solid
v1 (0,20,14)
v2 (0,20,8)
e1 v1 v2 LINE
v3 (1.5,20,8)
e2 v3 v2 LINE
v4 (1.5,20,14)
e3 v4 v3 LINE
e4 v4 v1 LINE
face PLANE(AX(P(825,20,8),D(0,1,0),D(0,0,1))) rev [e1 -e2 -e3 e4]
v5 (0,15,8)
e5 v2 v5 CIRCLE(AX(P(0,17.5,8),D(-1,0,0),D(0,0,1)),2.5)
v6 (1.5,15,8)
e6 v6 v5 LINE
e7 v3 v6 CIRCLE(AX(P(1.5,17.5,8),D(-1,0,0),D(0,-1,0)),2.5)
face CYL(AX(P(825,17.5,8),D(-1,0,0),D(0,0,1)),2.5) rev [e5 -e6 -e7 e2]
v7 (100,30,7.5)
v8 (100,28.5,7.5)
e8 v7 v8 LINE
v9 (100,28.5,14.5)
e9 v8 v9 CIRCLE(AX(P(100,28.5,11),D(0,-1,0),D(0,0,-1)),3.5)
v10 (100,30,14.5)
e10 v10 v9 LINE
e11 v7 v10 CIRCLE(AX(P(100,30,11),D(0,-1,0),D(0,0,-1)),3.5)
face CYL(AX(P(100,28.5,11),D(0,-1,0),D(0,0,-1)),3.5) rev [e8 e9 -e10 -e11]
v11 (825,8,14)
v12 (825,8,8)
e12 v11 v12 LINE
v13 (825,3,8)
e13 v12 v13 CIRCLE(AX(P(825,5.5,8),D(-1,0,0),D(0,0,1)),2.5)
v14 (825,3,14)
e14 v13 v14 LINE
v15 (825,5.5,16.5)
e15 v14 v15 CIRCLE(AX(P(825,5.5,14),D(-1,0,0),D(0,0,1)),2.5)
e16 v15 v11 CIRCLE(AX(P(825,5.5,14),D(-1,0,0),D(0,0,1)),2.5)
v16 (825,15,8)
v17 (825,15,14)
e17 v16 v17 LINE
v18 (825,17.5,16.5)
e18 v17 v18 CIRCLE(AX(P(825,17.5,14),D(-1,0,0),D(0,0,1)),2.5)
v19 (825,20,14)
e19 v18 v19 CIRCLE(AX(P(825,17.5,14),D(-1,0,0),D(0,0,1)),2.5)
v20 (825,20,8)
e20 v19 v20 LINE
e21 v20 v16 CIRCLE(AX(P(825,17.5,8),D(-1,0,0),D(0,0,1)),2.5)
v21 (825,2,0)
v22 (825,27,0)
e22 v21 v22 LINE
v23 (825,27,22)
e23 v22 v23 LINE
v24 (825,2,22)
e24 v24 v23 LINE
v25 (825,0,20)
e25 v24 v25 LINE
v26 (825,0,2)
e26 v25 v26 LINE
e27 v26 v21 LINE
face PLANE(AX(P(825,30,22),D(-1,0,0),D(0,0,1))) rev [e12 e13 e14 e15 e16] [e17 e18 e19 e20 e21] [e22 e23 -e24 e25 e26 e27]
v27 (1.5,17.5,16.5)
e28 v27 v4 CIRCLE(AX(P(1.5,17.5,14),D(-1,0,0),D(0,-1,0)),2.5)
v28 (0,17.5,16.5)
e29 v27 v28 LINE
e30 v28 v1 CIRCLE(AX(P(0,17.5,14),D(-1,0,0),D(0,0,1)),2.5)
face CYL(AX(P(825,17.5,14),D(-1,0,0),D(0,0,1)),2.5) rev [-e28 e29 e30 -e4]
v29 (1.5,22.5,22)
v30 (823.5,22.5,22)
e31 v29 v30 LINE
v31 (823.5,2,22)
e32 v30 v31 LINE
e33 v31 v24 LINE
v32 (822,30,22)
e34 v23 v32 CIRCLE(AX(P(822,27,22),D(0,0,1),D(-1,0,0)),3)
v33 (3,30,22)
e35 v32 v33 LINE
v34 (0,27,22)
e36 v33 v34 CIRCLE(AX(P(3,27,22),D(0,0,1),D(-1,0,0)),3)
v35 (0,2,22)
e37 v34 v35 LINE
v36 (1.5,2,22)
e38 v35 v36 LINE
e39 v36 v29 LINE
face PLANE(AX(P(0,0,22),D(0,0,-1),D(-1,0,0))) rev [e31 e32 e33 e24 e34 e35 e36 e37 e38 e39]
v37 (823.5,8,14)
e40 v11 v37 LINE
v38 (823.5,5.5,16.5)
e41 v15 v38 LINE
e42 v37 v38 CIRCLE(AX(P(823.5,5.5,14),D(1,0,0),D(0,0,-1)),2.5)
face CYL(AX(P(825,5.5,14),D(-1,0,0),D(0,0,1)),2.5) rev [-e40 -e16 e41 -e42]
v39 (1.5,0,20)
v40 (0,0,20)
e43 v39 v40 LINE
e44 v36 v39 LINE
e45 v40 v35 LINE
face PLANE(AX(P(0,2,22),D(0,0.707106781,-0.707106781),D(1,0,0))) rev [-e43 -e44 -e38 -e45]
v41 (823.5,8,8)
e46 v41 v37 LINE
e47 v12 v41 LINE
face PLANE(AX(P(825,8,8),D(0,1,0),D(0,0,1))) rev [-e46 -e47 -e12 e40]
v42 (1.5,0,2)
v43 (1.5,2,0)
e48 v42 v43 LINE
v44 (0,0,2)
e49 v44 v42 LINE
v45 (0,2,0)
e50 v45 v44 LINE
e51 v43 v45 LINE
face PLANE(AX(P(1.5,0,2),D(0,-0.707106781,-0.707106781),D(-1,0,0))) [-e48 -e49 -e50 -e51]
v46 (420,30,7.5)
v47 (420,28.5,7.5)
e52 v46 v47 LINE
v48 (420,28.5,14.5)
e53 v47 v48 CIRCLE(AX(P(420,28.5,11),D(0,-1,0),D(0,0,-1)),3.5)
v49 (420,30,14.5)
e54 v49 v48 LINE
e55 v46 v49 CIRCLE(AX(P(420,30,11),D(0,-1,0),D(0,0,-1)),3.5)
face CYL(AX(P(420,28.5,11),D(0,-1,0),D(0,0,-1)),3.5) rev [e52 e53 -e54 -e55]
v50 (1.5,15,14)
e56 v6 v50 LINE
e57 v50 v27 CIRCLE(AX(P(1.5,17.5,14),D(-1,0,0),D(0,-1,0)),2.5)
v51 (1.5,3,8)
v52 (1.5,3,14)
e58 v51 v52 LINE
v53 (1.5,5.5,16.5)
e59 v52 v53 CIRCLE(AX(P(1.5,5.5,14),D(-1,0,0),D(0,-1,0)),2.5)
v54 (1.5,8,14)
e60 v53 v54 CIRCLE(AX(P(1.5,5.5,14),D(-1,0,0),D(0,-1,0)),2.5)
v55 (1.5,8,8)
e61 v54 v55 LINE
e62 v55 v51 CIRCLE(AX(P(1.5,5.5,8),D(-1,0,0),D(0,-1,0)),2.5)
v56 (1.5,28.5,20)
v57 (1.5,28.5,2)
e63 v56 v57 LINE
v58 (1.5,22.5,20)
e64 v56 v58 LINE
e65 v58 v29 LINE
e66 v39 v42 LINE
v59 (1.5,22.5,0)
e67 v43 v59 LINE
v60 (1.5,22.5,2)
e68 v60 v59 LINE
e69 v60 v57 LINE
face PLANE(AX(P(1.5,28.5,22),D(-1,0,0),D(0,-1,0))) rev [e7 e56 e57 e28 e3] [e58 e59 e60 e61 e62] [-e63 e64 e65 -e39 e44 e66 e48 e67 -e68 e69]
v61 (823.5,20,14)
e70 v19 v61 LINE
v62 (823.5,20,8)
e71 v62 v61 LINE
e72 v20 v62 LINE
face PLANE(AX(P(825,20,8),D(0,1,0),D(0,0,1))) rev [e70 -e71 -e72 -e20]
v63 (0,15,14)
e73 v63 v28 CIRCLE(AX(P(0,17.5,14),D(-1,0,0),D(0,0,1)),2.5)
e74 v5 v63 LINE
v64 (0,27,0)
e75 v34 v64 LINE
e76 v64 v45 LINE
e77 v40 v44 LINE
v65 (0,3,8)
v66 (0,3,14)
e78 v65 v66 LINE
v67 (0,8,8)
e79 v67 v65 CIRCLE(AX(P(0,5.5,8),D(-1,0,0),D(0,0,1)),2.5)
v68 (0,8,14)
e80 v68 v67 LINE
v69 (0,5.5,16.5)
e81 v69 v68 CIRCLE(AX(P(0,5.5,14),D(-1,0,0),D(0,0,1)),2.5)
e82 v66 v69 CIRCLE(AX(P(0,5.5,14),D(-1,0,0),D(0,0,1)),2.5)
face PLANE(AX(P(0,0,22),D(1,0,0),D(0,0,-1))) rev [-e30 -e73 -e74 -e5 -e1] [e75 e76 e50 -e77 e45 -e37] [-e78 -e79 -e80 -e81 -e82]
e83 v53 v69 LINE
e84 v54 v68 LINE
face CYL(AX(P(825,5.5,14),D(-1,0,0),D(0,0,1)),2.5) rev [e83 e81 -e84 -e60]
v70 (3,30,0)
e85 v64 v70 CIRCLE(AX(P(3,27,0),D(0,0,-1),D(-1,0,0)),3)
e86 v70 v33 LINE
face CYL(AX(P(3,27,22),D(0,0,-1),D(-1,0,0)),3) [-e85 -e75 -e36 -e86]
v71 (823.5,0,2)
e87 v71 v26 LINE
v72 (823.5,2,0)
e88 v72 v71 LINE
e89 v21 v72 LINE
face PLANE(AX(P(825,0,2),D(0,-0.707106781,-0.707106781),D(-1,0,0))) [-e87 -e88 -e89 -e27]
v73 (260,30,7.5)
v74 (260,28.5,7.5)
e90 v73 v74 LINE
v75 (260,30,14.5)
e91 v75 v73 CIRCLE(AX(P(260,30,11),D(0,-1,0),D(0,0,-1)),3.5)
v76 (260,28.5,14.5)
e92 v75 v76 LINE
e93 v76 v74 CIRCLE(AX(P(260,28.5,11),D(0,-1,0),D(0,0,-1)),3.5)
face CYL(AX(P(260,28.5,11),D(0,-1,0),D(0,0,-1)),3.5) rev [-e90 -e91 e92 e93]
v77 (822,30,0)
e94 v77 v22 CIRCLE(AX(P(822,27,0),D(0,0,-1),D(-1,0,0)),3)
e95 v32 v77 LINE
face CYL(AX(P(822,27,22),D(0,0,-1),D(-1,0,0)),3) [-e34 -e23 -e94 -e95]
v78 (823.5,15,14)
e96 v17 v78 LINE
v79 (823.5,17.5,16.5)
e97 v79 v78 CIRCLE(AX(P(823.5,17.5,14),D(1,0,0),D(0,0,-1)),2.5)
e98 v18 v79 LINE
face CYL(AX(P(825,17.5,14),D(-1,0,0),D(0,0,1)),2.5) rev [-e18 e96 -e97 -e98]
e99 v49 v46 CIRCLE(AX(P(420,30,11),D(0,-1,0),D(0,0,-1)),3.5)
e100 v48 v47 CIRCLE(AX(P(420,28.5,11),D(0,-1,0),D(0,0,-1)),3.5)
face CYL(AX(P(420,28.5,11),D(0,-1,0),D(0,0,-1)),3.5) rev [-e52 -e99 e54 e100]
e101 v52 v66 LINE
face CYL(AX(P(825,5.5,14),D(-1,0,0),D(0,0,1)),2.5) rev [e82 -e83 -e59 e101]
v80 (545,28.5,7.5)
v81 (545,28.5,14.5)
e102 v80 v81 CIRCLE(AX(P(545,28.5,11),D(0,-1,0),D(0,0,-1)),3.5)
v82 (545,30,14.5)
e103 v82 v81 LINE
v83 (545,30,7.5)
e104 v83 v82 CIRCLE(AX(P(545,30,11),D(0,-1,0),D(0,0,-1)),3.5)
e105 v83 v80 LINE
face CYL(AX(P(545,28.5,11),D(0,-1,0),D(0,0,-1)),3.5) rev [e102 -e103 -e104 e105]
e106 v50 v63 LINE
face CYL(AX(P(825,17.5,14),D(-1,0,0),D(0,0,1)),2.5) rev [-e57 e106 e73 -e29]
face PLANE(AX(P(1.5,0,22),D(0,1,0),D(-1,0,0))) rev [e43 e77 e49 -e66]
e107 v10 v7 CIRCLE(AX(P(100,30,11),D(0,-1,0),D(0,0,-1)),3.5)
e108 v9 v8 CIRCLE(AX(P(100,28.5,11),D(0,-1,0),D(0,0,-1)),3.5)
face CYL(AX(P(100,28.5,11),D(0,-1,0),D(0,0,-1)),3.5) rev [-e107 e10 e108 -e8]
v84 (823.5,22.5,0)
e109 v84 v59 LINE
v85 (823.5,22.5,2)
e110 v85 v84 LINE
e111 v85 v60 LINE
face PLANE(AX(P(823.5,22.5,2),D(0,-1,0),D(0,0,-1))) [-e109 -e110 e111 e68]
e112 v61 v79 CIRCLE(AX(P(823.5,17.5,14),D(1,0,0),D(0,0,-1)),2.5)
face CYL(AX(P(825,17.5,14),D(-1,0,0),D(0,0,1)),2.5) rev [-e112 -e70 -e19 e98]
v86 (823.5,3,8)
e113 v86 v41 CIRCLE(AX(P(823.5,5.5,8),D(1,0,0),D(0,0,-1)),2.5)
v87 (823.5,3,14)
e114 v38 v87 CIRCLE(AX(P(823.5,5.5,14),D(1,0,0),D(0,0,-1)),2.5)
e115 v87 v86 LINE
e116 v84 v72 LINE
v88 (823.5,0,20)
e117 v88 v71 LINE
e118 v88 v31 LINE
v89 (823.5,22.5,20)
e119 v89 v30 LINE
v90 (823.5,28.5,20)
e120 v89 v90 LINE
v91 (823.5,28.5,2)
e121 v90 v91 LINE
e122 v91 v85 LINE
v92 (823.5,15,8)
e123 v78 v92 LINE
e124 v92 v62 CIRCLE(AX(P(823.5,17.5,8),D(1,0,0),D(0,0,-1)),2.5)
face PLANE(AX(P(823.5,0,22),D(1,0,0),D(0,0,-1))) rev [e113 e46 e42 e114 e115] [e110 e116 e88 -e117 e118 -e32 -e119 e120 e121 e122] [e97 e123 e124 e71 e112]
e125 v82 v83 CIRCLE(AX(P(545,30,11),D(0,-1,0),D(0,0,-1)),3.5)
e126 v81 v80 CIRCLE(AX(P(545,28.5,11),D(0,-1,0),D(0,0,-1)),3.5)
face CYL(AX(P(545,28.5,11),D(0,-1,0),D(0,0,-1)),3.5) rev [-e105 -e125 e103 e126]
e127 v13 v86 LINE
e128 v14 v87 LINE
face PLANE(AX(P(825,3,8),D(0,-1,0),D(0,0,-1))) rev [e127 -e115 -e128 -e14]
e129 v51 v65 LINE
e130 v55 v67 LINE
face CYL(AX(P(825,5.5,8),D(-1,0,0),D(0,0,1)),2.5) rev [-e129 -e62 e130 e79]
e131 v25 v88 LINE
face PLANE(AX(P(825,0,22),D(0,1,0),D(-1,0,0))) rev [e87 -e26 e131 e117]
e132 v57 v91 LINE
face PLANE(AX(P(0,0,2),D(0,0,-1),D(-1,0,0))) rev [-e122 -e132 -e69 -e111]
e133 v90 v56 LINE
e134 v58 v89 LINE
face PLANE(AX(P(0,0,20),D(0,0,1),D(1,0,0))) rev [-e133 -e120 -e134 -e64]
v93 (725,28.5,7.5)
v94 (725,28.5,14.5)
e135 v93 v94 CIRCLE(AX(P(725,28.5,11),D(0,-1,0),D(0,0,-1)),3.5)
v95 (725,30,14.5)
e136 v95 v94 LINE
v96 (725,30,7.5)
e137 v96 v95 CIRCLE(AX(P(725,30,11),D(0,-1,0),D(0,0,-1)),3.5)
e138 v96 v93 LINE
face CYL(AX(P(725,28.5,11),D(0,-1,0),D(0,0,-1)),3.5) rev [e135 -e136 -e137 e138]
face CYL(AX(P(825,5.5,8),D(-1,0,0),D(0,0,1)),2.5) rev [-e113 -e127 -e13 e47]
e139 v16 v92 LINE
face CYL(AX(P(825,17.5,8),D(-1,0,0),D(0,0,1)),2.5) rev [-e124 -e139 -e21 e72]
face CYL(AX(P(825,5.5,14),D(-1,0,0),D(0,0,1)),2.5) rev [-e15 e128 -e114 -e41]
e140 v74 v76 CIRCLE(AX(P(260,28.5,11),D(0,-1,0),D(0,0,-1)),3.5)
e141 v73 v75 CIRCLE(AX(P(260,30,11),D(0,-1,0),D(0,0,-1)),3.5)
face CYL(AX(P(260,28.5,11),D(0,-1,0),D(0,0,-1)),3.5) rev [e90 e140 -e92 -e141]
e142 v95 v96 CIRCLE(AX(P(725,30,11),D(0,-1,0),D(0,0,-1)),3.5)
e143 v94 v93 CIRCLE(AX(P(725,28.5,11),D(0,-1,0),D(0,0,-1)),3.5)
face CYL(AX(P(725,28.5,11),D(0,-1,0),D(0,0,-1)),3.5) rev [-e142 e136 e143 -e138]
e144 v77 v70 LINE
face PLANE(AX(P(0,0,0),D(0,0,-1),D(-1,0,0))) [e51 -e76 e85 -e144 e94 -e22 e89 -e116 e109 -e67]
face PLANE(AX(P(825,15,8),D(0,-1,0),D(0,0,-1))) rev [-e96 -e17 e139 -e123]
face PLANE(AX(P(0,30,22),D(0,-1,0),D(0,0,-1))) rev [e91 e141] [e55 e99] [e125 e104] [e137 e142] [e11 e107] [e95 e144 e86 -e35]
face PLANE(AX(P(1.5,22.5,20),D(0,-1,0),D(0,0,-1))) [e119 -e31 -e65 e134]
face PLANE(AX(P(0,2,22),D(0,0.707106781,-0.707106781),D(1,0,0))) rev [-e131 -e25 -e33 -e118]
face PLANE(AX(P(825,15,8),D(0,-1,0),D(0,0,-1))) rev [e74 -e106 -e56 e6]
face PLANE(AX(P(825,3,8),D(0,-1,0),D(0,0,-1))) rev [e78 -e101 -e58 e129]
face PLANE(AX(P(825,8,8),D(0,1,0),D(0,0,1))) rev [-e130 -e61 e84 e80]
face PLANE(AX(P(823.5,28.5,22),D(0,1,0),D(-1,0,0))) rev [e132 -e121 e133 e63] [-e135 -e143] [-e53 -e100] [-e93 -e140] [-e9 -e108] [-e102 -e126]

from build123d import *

# Parameters (mm, degrees)
EXTRUDE_1_DEPTH       = 22
SKETCH_2_W            = 822
SKETCH_2_H            = 6
EXTRUDE_2_DEPTH       = 2
SKETCH_3_W            = 822
SKETCH_3_H            = 6
EXTRUDE_3_DEPTH       = 2
CUT_EXTRUDE_1_DEPTH   = 826.838361909
CHAMFER_1_SIZE        = 2
FILLET_1_R            = 3
HOLE_WIZARD_7_0_7_1_D = 7


with BuildPart() as part:
    # 草图1 → 凸台-拉伸1 (new body)
    with BuildSketch(Plane.XY):
        Polygon((0, 0), (0, 30), (825, 30), (825, 0), (823.5, 0), (823.5, 28.5), (1.5, 28.5), (1.5, 0), align=None)
    extrude(amount=EXTRUDE_1_DEPTH)

    # 草图2 → 凸台-拉伸2 (add)
    with BuildSketch(Plane.XY.offset(22)):
        with Locations((412.5, 25.5)):
            Rectangle(SKETCH_2_W, SKETCH_2_H)
    extrude(amount=-EXTRUDE_2_DEPTH)

    # 草图3 → 凸台-拉伸3 (add)
    with BuildSketch(Plane(origin=(0, 0, 0), x_dir=(-1, 0, 0), z_dir=(0, 0, -1))):
        with Locations((-412.5, 25.5)):
            Rectangle(SKETCH_3_W, SKETCH_3_H)
    extrude(amount=-EXTRUDE_3_DEPTH)

    # 草图5 → 切除-拉伸1 (cut, through all)
    with BuildSketch(Plane.ZY):
        with BuildLine():
            Line((8, 20), (14, 20))
            ThreePointArc((14, 20), (16.5, 17.5), (14, 15))
            Line((14, 15), (8, 15))
            ThreePointArc((8, 15), (5.5, 17.5), (8, 20))
        make_face()
        with BuildLine():
            Line((8, 8), (14, 8))
            ThreePointArc((14, 8), (16.5, 5.5), (14, 3))
            Line((14, 3), (8, 3))
            ThreePointArc((8, 3), (5.5, 5.5), (8, 8))
        make_face()
    extrude(amount=-CUT_EXTRUDE_1_DEPTH, mode=Mode.SUBTRACT)

    # 倒角1
    chamfer_1_edges = [part.edges().sort_by_distance(p)[0] for p in [
        (0.75, 0, 0),
        (824.25, 0, 22),
        (0.75, 0, 22),
        (824.25, 0, 0),
    ]]
    chamfer(chamfer_1_edges, length=CHAMFER_1_SIZE)

    # 圆角1
    fillet_1_edges = [part.edges().sort_by_distance(p)[0] for p in [
        (0, 30, 11),
        (825, 30, 11),
    ]]
    fillet(fillet_1_edges, radius=FILLET_1_R)

    # Ø7.0 (7) 直径孔1 (through all)
    with Locations(Plane(origin=(0, 28.5, 0), x_dir=(-1, 0, 0), z_dir=(0, -1, 0))):
        with Locations((-100, -11), (-260, -11), (-420, -11), (-545, -11), (-725, -11)):
            Hole(HOLE_WIZARD_7_0_7_1_D / 2)


solid = part.part
